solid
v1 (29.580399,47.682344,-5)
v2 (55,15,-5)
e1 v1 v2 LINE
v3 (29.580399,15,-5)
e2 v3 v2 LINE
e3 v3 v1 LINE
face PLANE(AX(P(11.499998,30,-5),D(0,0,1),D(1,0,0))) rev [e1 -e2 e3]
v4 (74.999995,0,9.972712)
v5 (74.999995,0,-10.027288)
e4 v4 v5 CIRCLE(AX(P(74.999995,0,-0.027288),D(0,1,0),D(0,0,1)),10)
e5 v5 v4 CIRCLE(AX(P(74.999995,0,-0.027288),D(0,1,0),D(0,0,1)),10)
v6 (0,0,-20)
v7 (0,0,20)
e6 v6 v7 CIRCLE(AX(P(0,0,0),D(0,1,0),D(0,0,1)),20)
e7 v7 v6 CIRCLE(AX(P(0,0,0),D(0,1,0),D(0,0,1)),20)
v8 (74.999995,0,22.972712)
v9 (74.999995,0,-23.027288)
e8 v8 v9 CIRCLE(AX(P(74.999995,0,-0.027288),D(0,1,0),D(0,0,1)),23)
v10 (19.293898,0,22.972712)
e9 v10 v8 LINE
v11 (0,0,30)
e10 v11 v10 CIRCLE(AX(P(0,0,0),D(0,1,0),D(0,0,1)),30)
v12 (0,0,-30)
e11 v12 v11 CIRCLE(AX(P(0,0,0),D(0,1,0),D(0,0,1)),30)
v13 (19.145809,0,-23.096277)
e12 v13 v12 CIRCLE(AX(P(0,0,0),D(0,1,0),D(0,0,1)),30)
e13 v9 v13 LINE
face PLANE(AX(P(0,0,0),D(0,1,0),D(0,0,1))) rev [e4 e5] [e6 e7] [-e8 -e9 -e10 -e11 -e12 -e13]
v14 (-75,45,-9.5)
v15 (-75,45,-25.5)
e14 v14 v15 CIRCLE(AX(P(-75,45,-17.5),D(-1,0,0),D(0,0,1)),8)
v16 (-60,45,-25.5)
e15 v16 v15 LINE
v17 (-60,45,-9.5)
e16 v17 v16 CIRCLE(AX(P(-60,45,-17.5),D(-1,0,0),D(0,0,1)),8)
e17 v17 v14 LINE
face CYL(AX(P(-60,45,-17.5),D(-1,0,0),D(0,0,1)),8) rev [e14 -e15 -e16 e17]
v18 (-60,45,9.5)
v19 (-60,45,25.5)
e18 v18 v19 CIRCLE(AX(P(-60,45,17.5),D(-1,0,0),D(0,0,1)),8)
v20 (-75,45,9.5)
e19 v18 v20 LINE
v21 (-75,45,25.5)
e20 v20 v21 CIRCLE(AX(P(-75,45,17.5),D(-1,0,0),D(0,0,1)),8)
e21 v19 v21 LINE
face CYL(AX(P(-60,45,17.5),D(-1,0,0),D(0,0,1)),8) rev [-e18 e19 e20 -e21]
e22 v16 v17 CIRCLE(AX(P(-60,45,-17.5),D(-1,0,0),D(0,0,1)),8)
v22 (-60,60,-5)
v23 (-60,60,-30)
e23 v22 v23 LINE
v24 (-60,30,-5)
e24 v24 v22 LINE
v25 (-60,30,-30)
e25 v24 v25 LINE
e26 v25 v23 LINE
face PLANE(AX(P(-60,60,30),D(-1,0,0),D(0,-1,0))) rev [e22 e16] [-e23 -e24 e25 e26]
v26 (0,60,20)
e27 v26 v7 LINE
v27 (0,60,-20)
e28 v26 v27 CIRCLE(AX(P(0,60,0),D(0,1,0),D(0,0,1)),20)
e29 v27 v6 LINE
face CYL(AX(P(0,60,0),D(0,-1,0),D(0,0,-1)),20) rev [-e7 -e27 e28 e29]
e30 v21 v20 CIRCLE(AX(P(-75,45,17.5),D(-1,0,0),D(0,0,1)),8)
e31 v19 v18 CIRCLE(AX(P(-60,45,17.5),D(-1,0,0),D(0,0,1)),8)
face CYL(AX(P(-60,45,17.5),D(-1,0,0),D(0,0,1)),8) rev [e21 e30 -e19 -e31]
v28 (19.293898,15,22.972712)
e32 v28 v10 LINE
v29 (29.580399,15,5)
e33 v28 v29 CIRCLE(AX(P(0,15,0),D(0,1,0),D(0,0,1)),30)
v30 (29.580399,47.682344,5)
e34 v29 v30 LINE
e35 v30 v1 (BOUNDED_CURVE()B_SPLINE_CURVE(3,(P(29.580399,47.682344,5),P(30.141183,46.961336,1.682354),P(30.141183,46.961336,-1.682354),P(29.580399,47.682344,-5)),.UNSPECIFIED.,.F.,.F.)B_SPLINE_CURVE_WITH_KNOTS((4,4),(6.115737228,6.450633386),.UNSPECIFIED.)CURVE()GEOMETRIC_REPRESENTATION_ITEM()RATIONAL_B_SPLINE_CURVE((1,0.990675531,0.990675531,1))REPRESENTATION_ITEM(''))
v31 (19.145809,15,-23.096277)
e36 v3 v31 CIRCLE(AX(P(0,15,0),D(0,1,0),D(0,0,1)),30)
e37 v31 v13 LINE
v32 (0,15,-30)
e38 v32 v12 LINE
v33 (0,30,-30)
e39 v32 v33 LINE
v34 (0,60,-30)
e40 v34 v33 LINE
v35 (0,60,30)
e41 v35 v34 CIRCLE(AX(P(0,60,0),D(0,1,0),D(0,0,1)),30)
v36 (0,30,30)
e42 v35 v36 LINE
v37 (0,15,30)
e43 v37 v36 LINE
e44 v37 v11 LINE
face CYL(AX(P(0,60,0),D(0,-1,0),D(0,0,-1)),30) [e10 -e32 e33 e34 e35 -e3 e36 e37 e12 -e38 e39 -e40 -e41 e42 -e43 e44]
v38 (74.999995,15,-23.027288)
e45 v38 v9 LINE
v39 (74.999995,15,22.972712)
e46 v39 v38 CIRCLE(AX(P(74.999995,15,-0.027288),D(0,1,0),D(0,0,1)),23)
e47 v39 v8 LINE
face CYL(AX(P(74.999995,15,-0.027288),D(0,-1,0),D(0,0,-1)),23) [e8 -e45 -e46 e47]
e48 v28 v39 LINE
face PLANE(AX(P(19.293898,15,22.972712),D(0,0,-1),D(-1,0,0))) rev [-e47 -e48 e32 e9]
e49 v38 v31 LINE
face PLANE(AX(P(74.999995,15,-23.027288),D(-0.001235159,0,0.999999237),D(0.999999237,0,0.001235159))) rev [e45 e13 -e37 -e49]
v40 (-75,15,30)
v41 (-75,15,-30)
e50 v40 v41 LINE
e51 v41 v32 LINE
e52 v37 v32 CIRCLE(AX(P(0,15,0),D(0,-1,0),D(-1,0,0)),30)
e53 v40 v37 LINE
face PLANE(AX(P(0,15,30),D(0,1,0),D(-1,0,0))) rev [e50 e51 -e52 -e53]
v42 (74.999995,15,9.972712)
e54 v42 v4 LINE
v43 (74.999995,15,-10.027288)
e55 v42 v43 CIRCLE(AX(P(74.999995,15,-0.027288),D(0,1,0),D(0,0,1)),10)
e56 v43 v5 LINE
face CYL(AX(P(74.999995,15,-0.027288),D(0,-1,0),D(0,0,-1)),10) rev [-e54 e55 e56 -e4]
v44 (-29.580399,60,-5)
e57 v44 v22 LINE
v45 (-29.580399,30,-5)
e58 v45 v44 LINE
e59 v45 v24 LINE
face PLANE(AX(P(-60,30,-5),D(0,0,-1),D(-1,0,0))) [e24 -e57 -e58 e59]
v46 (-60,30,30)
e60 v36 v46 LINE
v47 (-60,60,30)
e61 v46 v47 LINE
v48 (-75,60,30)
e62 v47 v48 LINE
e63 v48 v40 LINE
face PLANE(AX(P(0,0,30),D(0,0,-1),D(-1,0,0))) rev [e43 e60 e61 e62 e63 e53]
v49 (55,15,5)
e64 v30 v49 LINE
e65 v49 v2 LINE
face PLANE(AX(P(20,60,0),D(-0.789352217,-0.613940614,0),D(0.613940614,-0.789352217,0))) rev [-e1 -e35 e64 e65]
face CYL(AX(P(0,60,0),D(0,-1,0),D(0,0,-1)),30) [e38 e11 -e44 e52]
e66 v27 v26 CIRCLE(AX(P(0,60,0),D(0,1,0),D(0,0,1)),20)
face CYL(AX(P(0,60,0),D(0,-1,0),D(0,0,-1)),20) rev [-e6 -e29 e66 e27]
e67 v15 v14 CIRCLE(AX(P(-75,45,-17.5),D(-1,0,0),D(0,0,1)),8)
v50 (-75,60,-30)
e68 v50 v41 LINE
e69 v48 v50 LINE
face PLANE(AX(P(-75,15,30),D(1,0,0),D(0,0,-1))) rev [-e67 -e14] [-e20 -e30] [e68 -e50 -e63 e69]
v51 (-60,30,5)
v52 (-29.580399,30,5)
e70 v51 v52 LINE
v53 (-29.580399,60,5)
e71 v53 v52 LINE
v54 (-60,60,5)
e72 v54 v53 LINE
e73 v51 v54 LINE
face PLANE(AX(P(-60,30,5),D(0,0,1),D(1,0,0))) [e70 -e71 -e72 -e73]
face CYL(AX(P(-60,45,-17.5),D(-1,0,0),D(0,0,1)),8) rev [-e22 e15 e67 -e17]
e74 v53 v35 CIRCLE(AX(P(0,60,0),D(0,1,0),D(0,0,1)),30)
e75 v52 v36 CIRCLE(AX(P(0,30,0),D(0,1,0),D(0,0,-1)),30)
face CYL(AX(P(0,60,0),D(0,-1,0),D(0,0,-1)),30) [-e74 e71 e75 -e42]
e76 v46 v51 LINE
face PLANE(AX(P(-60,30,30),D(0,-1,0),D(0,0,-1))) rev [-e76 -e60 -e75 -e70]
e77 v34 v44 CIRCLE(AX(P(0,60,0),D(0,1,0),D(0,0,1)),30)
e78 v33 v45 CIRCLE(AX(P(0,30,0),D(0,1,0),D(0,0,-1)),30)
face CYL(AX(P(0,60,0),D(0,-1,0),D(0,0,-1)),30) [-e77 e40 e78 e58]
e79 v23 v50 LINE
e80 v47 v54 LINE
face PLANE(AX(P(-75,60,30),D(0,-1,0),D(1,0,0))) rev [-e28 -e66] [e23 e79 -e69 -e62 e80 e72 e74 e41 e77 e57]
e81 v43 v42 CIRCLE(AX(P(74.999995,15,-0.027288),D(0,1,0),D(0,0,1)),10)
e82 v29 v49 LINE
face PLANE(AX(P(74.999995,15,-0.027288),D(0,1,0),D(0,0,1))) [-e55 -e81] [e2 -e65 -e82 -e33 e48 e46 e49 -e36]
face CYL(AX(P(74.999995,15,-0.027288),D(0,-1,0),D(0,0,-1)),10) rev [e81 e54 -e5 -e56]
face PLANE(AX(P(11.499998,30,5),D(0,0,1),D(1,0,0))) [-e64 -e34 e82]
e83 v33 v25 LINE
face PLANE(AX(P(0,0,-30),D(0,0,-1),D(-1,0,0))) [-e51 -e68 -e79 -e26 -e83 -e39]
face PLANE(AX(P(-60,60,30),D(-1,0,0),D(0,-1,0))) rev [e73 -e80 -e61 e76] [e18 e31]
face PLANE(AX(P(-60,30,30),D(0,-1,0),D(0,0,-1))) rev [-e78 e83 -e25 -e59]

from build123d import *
from build123d.topology import SkipClean

# Parameters (mm, degrees)
BASE_BRACKET_DEPTH        = 30
HUB_BOSS_SKETCH_R         = 30
HUB_BOSS_SKETCH_R_2       = 20
HUB_BOSS_DEPTH            = 60
LUG_ARM_SKETCH_R          = 10
LUG_ARM_DEPTH             = 15
CONNECTING_WEB_SKETCH_W   = 40
CONNECTING_WEB_SKETCH_H   = 10
CONNECTING_WEB_DEPTH      = 30
HUB_START                 = -60
HUB_BORE_SKETCH_R         = 20
HUB_BORE_DEPTH            = 60
SUPPORT_RIB_REACH         = 120.76
SUPPORT_RIB_SKETCH_WALL_W = 296.52928849
SUPPORT_RIB_SKETCH_WALL_H = 10
SIDE_WALL_HOLES_SKETCH_R  = 8
SIDE_WALL_HOLES_DEPTH     = 15


with BuildPart() as part:
    # Base Bracket Profile Sketch → Base Bracket (new, symmetric)
    with BuildSketch(Plane.XY):
        Polygon((0, 15), (-75, 15), (-75, 60), (-60, 60), (-60, 30), (0, 30), align=None)
    extrude(amount=BASE_BRACKET_DEPTH, both=True)

    # Hub Boss Sketch → Hub Boss (add)
    with BuildSketch(Plane(origin=(0, 0, 0), x_dir=(1, 0, 0), z_dir=(0, 1, 0))):
        with Locations(Location((0, 0, 0), (0, 0, 270))):
            Circle(HUB_BOSS_SKETCH_R)
        with Locations(Location((0, 0, 0), (0, 0, 270))):
            Circle(HUB_BOSS_SKETCH_R_2, mode=Mode.SUBTRACT)
    extrude(amount=HUB_BOSS_DEPTH)

    # Lug Arm Sketch → Lug Arm (add)
    with BuildSketch(Plane(origin=(0, 0, 0), x_dir=(1, 0, 0), z_dir=(0, 1, 0))):
        with BuildLine():
            Line((74.999995036, 23.027288115), (19.14580869, 23.096276964))
            Line((19.14580869, 23.096276964), (19.293898223, 5.267398918))
            ThreePointArc((19.293898223, 5.267398918), (20, 0), (19.293898223, -5.267398918))
            Line((19.293898223, -5.267398918), (19.293898223, -22.972711885))
            Line((19.293898223, -22.972711885), (74.999995036, -22.972711885))
            ThreePointArc((74.999995036, -22.972711885), (97.999995036, 0.027288115), (74.999995036, 23.027288115))
        make_face()
        with Locations(Location((74.999995036, 0.027288115, 0), (0, 0, 270))):
            Circle(LUG_ARM_SKETCH_R, mode=Mode.SUBTRACT)
    extrude(amount=LUG_ARM_DEPTH)

    # Connecting Web Sketch → Connecting Web (add)
    with BuildSketch(Plane(origin=(0, 60, 0), x_dir=(1, 0, 0), z_dir=(0, 1, 0))):
        with Locations((-40, 0)):
            Rectangle(CONNECTING_WEB_SKETCH_W, CONNECTING_WEB_SKETCH_H)
    extrude(amount=-CONNECTING_WEB_DEPTH)

    # Hub Bore Sketch → Hub Bore (cut)
    with SkipClean():  # the faces are left unmerged after this step: merging them gives an invalid solid
        with BuildSketch(Plane(origin=(0, 60, 0), x_dir=(1, 0, 0), z_dir=(0, 1, 0)).offset(HUB_START)):
            with Locations(Location((0, 0, 0), (0, 0, 270))):
                Circle(HUB_BORE_SKETCH_R)
        extrude(amount=HUB_BORE_DEPTH, mode=Mode.SUBTRACT)

    # Support Rib Sketch wall → Support Rib (add, up to next)
    with BuildSketch(Plane(origin=(37.5, 37.5, 0), x_dir=(0.613940613515, -0.789352217376, 0), z_dir=(0.789352217376, 0.613940613515, 0)), mode=Mode.PRIVATE) as support_rib_sk1:
        Rectangle(SUPPORT_RIB_SKETCH_WALL_W, SUPPORT_RIB_SKETCH_WALL_H)
    support_rib_tool1 = extrude(support_rib_sk1.sketch, amount=-SUPPORT_RIB_REACH, mode=Mode.PRIVATE) - part.part
    add(support_rib_tool1.solids().sort_by_distance((37.5, 37.5, 0))[0])

    # Side Wall Holes Sketch → Side Wall Holes (cut)
    with SkipClean():  # the faces are left unmerged after this step: merging them gives an invalid solid
        with BuildSketch(Plane.ZY.offset(75)):
            with Locations((-17.5, 45)):
                Circle(SIDE_WALL_HOLES_SKETCH_R)
            with Locations((17.5, 45)):
                Circle(SIDE_WALL_HOLES_SKETCH_R)
        extrude(amount=-SIDE_WALL_HOLES_DEPTH, mode=Mode.SUBTRACT)


solid = part.part
